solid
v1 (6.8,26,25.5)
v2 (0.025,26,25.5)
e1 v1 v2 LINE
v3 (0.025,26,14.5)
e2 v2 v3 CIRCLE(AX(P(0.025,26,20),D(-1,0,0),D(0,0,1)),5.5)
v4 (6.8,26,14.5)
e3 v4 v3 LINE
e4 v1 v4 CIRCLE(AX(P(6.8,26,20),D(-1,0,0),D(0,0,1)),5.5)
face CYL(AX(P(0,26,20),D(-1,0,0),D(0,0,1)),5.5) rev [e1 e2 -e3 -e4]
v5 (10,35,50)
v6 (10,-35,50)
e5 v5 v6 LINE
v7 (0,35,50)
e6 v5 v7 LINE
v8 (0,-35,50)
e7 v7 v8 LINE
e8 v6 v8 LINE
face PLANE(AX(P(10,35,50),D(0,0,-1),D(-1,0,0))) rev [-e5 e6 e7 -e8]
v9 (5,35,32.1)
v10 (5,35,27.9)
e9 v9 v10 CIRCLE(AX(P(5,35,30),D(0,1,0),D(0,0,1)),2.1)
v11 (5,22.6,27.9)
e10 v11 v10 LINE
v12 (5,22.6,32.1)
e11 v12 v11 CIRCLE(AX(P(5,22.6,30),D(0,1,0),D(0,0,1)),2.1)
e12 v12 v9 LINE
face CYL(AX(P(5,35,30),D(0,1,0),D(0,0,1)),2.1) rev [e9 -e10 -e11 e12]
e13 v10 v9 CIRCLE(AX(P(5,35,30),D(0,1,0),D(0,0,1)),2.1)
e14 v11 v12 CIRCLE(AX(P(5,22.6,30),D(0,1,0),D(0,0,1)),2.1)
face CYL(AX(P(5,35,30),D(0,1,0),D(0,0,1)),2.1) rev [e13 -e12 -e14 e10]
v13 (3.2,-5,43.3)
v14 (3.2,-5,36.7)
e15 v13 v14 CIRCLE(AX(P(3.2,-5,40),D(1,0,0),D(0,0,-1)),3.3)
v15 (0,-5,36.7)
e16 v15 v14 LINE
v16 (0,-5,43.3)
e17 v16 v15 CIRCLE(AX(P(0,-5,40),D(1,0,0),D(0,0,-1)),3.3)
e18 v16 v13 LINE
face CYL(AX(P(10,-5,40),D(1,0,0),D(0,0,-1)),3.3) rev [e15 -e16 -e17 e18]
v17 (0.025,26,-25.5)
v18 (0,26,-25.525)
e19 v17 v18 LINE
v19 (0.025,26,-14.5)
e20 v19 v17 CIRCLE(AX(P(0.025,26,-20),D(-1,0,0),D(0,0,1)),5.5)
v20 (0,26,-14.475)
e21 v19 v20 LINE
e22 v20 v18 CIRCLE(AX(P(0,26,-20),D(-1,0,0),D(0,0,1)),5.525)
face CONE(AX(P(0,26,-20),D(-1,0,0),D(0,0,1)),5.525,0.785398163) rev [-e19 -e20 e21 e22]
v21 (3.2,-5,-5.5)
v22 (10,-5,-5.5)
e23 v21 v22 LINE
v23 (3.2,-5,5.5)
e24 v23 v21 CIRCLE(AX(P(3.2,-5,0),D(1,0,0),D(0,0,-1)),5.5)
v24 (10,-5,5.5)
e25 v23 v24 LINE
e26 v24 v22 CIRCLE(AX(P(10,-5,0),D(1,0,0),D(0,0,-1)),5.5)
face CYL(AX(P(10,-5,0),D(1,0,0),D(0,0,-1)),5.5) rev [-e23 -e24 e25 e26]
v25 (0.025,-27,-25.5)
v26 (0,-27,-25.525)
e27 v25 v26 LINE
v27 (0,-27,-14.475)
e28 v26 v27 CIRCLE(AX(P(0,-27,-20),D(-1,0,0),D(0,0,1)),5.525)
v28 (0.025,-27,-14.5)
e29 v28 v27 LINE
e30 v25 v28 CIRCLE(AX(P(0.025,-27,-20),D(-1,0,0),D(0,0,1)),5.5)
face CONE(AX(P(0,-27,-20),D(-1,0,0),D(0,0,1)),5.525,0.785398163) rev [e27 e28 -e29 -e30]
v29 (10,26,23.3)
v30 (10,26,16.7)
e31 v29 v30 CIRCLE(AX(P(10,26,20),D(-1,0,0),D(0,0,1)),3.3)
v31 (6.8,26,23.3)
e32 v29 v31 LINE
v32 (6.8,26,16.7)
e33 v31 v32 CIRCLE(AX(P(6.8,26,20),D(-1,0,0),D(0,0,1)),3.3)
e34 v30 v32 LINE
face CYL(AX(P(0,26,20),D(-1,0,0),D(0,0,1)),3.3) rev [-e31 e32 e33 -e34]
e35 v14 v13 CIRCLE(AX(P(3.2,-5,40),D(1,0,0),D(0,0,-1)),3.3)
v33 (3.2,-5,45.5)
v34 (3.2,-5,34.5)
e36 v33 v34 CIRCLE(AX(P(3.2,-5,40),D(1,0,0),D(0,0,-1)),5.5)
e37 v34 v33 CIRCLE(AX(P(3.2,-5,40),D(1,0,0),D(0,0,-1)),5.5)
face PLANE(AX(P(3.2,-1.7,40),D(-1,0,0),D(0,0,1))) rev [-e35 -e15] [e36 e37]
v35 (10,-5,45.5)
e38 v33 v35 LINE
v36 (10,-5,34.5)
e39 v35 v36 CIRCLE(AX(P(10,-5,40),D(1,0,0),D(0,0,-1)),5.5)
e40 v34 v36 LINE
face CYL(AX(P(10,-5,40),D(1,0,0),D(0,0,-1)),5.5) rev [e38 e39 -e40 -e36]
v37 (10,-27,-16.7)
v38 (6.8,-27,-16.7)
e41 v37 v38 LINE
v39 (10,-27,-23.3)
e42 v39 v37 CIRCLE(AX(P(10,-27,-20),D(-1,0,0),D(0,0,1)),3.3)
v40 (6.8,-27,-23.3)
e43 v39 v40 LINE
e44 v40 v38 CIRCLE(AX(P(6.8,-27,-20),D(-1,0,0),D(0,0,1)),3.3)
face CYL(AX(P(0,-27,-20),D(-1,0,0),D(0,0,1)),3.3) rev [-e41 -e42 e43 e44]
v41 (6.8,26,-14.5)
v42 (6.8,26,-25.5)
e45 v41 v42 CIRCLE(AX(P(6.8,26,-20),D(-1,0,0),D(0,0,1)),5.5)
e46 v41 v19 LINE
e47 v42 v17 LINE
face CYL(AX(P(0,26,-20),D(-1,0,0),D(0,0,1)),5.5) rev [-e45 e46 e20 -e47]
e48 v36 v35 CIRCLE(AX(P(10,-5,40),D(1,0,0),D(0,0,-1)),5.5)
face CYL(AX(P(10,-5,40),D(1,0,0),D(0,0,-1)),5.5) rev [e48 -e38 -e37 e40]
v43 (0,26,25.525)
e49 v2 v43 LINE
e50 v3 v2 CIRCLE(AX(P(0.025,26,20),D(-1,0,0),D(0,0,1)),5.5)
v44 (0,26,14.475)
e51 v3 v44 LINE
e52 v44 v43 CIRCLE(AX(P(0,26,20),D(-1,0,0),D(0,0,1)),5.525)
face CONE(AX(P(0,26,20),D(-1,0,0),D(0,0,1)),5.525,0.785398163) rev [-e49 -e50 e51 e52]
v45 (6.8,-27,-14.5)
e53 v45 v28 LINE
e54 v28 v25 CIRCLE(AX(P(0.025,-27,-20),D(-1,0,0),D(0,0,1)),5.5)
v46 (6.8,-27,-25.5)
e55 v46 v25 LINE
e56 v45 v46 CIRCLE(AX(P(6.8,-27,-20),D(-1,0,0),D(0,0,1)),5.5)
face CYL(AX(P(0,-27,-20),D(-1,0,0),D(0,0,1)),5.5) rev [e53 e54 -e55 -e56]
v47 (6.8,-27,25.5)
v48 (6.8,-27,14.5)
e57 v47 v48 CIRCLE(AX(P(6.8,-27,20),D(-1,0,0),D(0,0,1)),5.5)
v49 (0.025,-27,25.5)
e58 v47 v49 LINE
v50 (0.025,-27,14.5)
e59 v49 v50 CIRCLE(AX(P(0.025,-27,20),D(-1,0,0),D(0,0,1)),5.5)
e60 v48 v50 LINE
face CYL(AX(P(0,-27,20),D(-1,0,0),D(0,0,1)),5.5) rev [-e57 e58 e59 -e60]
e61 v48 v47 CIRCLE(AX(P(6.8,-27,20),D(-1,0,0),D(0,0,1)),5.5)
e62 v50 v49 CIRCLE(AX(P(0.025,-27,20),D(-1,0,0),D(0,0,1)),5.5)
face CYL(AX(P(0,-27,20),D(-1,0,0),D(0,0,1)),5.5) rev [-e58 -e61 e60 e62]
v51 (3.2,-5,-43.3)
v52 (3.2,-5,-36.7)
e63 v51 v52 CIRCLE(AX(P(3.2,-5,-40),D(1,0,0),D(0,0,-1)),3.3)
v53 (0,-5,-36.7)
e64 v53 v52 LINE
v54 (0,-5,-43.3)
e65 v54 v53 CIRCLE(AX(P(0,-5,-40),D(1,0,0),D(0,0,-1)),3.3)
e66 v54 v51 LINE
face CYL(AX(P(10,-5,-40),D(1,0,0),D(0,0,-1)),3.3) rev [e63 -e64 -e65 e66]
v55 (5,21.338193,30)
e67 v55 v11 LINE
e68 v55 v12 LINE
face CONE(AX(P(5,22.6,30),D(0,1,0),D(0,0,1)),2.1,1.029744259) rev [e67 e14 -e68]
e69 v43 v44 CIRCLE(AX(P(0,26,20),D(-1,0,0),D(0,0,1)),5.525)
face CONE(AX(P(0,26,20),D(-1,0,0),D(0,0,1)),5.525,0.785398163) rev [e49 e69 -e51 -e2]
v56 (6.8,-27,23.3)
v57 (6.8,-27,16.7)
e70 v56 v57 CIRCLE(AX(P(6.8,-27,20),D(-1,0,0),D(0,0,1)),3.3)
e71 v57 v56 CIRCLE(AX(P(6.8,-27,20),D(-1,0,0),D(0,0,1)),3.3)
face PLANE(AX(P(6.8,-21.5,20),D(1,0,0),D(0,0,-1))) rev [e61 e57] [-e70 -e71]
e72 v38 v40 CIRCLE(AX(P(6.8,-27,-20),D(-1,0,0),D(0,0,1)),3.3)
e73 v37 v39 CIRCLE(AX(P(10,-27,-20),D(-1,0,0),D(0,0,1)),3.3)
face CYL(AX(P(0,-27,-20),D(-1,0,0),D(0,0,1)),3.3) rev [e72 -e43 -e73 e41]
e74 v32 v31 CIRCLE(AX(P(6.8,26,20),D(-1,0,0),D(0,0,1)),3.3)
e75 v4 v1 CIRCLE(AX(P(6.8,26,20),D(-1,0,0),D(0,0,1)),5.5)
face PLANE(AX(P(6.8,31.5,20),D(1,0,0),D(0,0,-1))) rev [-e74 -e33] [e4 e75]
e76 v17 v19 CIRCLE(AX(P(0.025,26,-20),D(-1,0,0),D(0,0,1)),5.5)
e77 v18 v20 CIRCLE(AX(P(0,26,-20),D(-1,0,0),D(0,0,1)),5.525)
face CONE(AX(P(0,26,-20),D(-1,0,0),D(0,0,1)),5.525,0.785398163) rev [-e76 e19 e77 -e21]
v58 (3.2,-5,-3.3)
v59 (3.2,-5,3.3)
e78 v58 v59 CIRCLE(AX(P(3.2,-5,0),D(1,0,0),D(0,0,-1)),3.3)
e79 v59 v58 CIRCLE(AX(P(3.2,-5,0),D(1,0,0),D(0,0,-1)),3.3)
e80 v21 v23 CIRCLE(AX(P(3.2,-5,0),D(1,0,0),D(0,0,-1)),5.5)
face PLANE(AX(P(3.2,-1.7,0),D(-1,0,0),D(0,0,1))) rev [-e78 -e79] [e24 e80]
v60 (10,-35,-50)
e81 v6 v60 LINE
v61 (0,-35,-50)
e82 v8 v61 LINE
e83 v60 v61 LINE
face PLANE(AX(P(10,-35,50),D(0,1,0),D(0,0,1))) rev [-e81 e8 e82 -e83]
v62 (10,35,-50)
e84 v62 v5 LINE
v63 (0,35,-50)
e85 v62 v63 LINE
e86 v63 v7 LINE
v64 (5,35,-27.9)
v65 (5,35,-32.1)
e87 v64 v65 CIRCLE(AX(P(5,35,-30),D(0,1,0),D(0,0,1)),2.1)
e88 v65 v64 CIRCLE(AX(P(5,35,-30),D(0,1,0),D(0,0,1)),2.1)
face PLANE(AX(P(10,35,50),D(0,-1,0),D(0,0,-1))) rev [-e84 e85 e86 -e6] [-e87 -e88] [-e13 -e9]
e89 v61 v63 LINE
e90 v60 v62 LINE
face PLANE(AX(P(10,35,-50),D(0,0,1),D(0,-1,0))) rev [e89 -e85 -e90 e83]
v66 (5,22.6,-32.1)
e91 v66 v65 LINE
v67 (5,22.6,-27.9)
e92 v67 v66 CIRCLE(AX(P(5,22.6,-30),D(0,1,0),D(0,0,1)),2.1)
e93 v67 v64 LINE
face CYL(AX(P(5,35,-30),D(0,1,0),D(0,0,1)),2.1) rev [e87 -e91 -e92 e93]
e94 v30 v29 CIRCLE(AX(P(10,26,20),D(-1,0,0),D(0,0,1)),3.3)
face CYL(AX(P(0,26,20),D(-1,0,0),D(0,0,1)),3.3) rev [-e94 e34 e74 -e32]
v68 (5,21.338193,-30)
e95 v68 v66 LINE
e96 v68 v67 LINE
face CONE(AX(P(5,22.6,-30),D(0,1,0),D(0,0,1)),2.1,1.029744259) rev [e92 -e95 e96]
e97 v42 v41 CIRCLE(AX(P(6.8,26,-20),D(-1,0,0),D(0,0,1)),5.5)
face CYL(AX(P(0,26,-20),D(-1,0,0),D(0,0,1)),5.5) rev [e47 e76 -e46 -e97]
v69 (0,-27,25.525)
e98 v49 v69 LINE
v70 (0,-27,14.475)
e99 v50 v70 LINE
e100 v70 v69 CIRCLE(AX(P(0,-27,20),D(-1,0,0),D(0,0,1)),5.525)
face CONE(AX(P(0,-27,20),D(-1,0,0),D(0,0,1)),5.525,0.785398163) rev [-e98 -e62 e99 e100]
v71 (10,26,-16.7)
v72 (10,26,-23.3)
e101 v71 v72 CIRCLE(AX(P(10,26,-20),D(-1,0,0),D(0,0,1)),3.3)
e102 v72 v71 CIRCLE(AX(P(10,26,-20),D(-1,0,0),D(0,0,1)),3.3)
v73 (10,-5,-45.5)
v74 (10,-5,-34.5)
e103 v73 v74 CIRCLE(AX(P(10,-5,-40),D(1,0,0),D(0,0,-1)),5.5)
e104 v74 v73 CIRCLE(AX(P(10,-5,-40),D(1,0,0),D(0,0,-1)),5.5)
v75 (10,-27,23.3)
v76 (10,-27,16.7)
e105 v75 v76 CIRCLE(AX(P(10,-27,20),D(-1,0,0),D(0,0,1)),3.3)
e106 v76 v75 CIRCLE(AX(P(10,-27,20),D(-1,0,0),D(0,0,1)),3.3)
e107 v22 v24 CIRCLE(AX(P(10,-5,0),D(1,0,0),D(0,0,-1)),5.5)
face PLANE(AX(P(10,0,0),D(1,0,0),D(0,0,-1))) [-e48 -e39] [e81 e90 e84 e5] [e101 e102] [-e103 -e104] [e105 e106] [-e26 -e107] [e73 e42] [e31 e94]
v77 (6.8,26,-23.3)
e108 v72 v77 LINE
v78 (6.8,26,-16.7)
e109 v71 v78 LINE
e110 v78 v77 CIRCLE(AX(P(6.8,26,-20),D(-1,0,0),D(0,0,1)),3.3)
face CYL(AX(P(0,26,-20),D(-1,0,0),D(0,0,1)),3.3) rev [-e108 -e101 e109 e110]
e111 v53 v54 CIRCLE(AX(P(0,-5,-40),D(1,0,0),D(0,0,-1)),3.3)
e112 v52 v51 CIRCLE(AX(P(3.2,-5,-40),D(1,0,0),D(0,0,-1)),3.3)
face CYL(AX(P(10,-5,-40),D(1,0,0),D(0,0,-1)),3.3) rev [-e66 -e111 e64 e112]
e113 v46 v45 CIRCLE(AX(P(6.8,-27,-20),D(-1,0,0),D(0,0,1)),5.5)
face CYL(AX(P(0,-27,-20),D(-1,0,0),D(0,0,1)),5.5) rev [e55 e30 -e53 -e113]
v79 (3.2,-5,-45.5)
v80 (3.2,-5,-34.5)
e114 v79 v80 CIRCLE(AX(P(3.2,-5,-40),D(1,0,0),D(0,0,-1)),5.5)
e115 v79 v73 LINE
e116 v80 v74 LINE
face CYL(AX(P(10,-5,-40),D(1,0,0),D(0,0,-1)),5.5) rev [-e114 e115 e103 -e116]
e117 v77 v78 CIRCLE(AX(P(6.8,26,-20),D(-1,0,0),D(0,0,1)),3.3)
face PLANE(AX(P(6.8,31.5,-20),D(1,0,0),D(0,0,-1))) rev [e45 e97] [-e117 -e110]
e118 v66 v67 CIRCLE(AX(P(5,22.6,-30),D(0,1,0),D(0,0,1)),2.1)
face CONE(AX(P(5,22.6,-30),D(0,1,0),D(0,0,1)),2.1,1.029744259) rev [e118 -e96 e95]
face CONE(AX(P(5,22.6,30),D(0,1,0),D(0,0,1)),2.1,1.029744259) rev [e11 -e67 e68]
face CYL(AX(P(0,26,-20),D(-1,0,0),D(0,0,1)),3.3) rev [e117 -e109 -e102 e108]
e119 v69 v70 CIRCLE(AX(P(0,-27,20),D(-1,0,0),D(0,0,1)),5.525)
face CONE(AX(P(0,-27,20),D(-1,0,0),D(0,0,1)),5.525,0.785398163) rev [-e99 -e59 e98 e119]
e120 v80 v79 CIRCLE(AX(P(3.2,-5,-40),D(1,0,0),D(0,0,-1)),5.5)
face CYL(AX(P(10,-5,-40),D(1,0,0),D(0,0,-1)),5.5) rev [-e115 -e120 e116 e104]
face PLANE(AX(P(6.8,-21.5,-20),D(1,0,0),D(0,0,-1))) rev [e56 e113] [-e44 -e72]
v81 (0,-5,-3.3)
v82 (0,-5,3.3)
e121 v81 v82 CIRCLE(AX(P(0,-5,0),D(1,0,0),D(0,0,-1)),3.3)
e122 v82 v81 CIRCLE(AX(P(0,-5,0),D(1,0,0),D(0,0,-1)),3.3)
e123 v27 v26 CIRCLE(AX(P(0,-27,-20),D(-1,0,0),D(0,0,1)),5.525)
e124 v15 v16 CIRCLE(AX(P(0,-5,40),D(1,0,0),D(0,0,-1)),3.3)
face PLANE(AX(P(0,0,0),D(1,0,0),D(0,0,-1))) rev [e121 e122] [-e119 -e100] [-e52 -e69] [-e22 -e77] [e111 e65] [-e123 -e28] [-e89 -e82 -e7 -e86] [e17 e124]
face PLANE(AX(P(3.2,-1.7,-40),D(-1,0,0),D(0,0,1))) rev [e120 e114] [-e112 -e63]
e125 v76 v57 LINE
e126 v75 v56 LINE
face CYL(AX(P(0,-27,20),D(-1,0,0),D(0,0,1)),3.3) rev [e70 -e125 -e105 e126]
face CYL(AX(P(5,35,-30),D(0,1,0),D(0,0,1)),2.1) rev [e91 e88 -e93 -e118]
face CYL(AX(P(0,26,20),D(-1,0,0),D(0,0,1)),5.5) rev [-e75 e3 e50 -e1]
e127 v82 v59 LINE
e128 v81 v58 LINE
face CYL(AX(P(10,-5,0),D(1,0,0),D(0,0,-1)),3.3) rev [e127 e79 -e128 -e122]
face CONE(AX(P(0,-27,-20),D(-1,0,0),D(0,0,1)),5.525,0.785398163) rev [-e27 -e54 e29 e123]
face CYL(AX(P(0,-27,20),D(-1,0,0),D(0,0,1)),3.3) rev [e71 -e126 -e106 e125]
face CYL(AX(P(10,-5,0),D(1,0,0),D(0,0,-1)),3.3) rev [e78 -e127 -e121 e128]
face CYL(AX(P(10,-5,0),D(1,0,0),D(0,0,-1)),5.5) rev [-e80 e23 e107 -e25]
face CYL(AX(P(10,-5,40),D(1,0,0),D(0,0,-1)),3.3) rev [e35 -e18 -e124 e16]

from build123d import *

# Parameters (mm, degrees)
SKETCH_1_W                = 100
SKETCH_1_H                = 70
EXTRUDE_1_DEPTH           = 10
HOLE_WIZARD_1_D           = 6.6
HOLE_WIZARD_1_DEPTH       = 15
HOLE_WIZARD_1_CBORE_D     = 11
HOLE_WIZARD_1_CBORE_DEPTH = 6.8
HOLE_WIZARD_1_TIP         = 1.982840043
HOLE_WIZARD_3_AT_2_COUNT  = 2
HOLE_WIZARD_3_AT_2_PITCH  = 40
HOLE_WIZARD_3_AT_3_COUNT  = 2
HOLE_WIZARD_3_AT_3_PITCH  = 53
HOLE_WIZARD_3_AT_4_COUNT  = 2
HOLE_WIZARD_3_AT_4_PITCH  = 66.400301204
HOLE_WIZARD_M5_1_D        = 4.2
HOLE_WIZARD_M5_1_DEPTH    = 12.4
HOLE_WIZARD_M5_1_TIP      = 1.2618073


with BuildPart() as part:
    # 草图1 → 凸台-拉伸1 (new body)
    with BuildSketch(Plane(origin=(0, 0, 0), x_dir=(0, 0, -1), z_dir=(1, 0, 0))):
        Rectangle(SKETCH_1_W, SKETCH_1_H)
    extrude(amount=EXTRUDE_1_DEPTH)

    # 打孔尺寸(%根据)内六角圆柱头螺钉的类型1
    with Locations(Plane(origin=(10, 0, 0), x_dir=(0, 0, -1), z_dir=(1, 0, 0))):
        with Locations((-40, -5), (0, -5), (40, -5)):
            CounterBoreHole(HOLE_WIZARD_1_D / 2, HOLE_WIZARD_1_CBORE_D / 2, HOLE_WIZARD_1_CBORE_DEPTH, depth=HOLE_WIZARD_1_DEPTH)
            with Locations((0, 0, -(HOLE_WIZARD_1_DEPTH + HOLE_WIZARD_1_TIP / 2))):  # 118° drill point
                Cone(0, HOLE_WIZARD_1_D / 2, HOLE_WIZARD_1_TIP, mode=Mode.SUBTRACT)

    # 草图9 → 打孔尺寸(%根据)内六角圆柱头螺钉的类型3 (revolve, cut)
    with BuildSketch(Plane(origin=(0, 26, -20), x_dir=(0, 0, 1), z_dir=(0, 1, 0))):
        Polygon((0, 0), (0, 10), (3.3, 10), (3.3, 6.8), (5.5, 6.8), (5.5, 0.025), (5.525, 0), align=None)
    hole_wizard_3 = revolve(axis=Axis((-6.35, 26, -20), (1, 0, 0)), mode=Mode.SUBTRACT)

    # 打孔尺寸(%根据)内六角圆柱头螺钉的类型3 at 2: 打孔尺寸(%根据)内六角圆柱头螺钉的类型3 ×2
    with Locations(*[(0, 0, i * HOLE_WIZARD_3_AT_2_PITCH) for i in range(1, HOLE_WIZARD_3_AT_2_COUNT)]):
        add(hole_wizard_3, mode=Mode.SUBTRACT)

    # 打孔尺寸(%根据)内六角圆柱头螺钉的类型3 at 3: 打孔尺寸(%根据)内六角圆柱头螺钉的类型3 ×2
    with Locations(*[(0, -i * HOLE_WIZARD_3_AT_3_PITCH, 0) for i in range(1, HOLE_WIZARD_3_AT_3_COUNT)]):
        add(hole_wizard_3, mode=Mode.SUBTRACT)

    # 打孔尺寸(%根据)内六角圆柱头螺钉的类型3 at 4: 打孔尺寸(%根据)内六角圆柱头螺钉的类型3 ×2
    with Locations(*[Vector(0, -0.7981891503332307, 0.6024069059118724) * (i * HOLE_WIZARD_3_AT_4_PITCH) for i in range(1, HOLE_WIZARD_3_AT_4_COUNT)]):
        add(hole_wizard_3, mode=Mode.SUBTRACT)

    # M5 螺纹孔1
    with Locations(Plane(origin=(0, 35, 0), x_dir=(1, 0, 0), z_dir=(0, 1, 0))):
        with Locations((5, 30), (5, -30)):
            Hole(HOLE_WIZARD_M5_1_D / 2, depth=HOLE_WIZARD_M5_1_DEPTH)
            with Locations((0, 0, -(HOLE_WIZARD_M5_1_DEPTH + HOLE_WIZARD_M5_1_TIP / 2))):  # 118° drill point
                Cone(0, HOLE_WIZARD_M5_1_D / 2, HOLE_WIZARD_M5_1_TIP, mode=Mode.SUBTRACT)


solid = part.part
